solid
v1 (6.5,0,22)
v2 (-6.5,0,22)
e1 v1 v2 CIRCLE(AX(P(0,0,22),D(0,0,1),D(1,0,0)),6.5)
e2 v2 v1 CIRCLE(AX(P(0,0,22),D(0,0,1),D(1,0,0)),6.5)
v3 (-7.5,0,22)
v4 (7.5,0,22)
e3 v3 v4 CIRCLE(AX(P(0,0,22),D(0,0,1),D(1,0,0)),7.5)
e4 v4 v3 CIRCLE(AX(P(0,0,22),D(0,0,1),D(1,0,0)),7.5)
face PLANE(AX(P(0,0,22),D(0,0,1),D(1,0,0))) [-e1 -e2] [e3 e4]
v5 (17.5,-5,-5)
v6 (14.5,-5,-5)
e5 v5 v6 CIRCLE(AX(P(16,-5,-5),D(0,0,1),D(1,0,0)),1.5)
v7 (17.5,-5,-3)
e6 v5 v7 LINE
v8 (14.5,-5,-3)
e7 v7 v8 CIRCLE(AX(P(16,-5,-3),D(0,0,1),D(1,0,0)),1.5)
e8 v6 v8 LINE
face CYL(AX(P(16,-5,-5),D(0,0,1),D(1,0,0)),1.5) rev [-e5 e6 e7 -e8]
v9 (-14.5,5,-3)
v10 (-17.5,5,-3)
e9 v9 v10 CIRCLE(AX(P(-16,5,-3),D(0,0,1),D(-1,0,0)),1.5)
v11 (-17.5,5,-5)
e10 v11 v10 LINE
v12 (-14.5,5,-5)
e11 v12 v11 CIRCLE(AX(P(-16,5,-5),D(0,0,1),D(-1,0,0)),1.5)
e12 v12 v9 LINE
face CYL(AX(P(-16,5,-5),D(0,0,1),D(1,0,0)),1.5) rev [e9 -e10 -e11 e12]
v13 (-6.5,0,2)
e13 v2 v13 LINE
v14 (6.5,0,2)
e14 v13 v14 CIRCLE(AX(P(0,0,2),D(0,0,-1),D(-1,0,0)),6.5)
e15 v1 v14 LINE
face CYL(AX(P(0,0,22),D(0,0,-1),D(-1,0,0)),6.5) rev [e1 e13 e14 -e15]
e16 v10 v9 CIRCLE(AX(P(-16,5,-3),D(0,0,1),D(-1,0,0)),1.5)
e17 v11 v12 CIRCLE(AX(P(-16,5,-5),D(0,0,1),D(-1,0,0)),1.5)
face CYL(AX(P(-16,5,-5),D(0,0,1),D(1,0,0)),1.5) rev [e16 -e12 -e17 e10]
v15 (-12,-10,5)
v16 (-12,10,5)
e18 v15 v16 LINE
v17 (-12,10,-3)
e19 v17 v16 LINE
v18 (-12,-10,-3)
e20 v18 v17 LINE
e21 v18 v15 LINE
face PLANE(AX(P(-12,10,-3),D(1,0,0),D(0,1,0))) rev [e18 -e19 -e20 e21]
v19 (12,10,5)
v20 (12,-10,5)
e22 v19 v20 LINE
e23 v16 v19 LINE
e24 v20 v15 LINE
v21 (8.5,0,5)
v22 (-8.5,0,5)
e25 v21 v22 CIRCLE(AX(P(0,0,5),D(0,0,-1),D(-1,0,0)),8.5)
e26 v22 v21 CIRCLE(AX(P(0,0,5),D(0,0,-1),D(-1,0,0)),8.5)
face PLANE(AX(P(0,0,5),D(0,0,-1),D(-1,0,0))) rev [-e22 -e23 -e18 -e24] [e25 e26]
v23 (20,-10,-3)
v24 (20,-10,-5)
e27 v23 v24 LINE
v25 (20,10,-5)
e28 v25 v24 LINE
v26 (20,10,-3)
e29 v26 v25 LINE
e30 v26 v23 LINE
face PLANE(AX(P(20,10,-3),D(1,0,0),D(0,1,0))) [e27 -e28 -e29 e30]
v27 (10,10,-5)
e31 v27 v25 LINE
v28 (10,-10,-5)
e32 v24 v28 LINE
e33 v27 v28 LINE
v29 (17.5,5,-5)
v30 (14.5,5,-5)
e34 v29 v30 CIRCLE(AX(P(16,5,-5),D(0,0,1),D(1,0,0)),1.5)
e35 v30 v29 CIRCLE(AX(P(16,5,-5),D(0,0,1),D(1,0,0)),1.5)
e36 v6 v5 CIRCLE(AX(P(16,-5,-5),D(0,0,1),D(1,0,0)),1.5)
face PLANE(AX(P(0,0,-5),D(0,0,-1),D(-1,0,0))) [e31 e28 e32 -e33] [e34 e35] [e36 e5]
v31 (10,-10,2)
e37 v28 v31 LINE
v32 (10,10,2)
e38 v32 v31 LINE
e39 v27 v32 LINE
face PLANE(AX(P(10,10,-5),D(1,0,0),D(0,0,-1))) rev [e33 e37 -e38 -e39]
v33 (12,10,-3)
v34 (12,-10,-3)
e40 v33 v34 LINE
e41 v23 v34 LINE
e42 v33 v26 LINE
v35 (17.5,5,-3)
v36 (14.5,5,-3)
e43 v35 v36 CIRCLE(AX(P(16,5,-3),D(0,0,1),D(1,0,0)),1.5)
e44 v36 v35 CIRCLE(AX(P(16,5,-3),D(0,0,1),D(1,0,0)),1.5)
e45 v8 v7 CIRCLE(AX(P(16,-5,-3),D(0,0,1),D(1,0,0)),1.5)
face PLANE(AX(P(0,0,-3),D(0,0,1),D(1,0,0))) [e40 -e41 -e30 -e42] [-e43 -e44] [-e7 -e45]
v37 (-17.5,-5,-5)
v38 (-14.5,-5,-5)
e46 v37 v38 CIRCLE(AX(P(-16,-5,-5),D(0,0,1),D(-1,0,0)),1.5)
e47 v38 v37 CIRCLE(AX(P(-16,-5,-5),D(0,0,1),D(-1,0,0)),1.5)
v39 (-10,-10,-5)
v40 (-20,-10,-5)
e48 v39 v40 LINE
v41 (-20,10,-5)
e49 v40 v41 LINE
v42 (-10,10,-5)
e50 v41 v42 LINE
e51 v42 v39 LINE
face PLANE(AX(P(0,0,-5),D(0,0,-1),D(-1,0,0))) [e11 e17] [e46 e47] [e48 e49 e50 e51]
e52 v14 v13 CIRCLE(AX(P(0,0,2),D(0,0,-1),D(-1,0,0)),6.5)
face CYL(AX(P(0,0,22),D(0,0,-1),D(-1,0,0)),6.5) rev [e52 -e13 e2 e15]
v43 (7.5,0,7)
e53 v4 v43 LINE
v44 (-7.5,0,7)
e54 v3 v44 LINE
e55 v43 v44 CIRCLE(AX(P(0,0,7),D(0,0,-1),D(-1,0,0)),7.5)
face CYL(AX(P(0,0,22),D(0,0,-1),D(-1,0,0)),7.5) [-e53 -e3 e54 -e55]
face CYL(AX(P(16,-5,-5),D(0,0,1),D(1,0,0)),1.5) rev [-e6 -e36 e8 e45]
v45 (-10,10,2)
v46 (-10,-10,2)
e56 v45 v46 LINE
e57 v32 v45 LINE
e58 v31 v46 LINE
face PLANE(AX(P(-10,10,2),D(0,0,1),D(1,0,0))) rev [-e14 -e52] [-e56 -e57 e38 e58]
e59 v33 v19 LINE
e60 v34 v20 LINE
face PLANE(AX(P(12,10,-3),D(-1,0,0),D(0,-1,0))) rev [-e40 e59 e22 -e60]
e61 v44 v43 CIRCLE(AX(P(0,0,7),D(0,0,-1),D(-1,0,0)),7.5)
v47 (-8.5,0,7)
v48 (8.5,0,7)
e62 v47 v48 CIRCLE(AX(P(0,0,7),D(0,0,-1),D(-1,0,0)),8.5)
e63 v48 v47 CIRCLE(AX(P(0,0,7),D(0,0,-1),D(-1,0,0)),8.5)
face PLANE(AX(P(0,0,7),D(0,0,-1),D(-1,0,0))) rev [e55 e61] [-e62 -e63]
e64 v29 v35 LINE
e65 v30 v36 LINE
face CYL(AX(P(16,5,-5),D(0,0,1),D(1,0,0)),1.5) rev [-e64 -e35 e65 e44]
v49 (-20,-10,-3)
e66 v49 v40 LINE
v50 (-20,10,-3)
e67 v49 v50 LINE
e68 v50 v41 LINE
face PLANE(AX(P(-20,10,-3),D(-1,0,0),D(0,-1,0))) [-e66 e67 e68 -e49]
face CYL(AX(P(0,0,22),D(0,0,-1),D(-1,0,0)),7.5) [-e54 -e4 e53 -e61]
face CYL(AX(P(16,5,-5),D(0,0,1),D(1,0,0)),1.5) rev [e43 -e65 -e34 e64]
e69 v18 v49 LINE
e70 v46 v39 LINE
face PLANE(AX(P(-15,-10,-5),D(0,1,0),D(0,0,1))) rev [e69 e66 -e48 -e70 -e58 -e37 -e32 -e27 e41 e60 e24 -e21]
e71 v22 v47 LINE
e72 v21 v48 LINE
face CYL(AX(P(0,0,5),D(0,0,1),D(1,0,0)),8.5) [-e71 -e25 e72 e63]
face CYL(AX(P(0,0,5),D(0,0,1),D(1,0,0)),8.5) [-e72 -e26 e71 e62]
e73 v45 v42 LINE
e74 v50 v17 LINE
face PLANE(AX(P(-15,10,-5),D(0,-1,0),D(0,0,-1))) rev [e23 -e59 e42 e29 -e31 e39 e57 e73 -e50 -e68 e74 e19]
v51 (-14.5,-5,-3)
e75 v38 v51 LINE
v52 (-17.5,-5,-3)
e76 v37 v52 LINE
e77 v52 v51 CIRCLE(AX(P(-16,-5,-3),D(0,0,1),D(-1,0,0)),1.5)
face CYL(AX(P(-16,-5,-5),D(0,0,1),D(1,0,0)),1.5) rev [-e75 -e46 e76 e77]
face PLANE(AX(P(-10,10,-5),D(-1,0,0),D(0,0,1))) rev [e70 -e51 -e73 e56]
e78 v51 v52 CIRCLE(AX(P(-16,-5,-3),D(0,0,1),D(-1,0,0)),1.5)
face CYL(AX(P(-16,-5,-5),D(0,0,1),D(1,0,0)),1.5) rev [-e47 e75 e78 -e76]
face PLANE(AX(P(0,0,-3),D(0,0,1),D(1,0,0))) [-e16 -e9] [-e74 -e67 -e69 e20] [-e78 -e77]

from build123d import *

# Parameters (mm, degrees)
SKETCH1_R           = 7.5
SKETCH1_R_2         = 6.5
BOSS_EXTRUDE1_DEPTH = 22
BOSS_EXTRUDE2_START = 2
SKETCH2_R           = 8.5
SKETCH2_R_2         = 7.5
BOSS_EXTRUDE2_DEPTH = 2
BOSS_EXTRUDE4_START = 2
SKETCH5_R           = 7.5
SKETCH5_R_2         = 6.5
BOSS_EXTRUDE4_DEPTH = 2
BOSS_EXTRUDE5_START = 2
SKETCH6_R           = 8.5
SKETCH6_R_2         = 6.5
BOSS_EXTRUDE5_DEPTH = 2
SKETCH7_W           = 30
SKETCH7_H           = 20
BOSS_EXTRUDE6_DEPTH = 10
SKETCH8_W           = 20
SKETCH8_H           = 7
CUT_EXTRUDE1_DEPTH  = 34.301651611
SKETCH9_W           = 5
SKETCH9_H           = 20
BOSS_EXTRUDE7_DEPTH = 2
SKETCH12_R          = 6.5
CUT_EXTRUDE3_DEPTH  = 31
SKETCH13_W          = 3
SKETCH13_H          = 20
CUT_EXTRUDE4_DEPTH  = 8
SKETCH11_R          = 1.5
CUT_EXTRUDE2_DEPTH  = 34.541019662


with BuildPart() as part:
    # Sketch1 → Boss-Extrude1 (new body)
    with BuildSketch(Plane.XY):
        Circle(SKETCH1_R)
        Circle(SKETCH1_R_2, mode=Mode.SUBTRACT)
    extrude(amount=BOSS_EXTRUDE1_DEPTH)

    # Sketch2 → Boss-Extrude2 (add)
    with BuildSketch(Plane(origin=(0, 0, 7), x_dir=(-1, 0, 0), z_dir=(0, 0, -1)).offset(BOSS_EXTRUDE2_START)):
        Circle(SKETCH2_R)
        Circle(SKETCH2_R_2, mode=Mode.SUBTRACT)
    extrude(amount=-BOSS_EXTRUDE2_DEPTH)

    # Sketch5 → Boss-Extrude4 (add)
    with BuildSketch(Plane(origin=(0, 0, 0), x_dir=(-1, 0, 0), z_dir=(0, 0, -1)).offset(BOSS_EXTRUDE4_START)):
        Circle(SKETCH5_R)
        Circle(SKETCH5_R_2, mode=Mode.SUBTRACT)
    extrude(amount=-BOSS_EXTRUDE4_DEPTH)

    # Sketch6 → Boss-Extrude5 (add)
    with BuildSketch(Plane(origin=(0, 0, -2), x_dir=(-1, 0, 0), z_dir=(0, 0, -1)).offset(BOSS_EXTRUDE5_START)):
        Circle(SKETCH6_R)
        Circle(SKETCH6_R_2, mode=Mode.SUBTRACT)
    extrude(amount=-BOSS_EXTRUDE5_DEPTH)

    # Sketch7 → Boss-Extrude6 (add)
    with BuildSketch(Plane(origin=(0, 0, 5), x_dir=(-1, 0, 0), z_dir=(0, 0, -1))):
        Rectangle(SKETCH7_W, SKETCH7_H)
    extrude(amount=BOSS_EXTRUDE6_DEPTH)

    # Sketch8 → Cut-Extrude1 (cut, through all)
    with BuildSketch(Plane.XZ.offset(10)):
        with Locations((0, -1.5)):
            Rectangle(SKETCH8_W, SKETCH8_H)
    extrude(amount=-CUT_EXTRUDE1_DEPTH, mode=Mode.SUBTRACT)

    # Sketch9 → Boss-Extrude7 (add)
    with BuildSketch(Plane(origin=(0, 0, -5), x_dir=(-1, 0, 0), z_dir=(0, 0, -1))):
        with Locations((-17.5, 0)):
            Rectangle(SKETCH9_W, SKETCH9_H)
        with Locations((17.5, 0)):
            Rectangle(SKETCH9_W, SKETCH9_H)
    extrude(amount=-BOSS_EXTRUDE7_DEPTH)

    # Sketch12 → Cut-Extrude3 (cut, through all)
    with BuildSketch(Plane(origin=(0, 0, 2), x_dir=(-1, 0, 0), z_dir=(0, 0, -1))):
        Circle(SKETCH12_R)
    extrude(amount=-CUT_EXTRUDE3_DEPTH, mode=Mode.SUBTRACT)

    # Sketch13 → Cut-Extrude4 (cut)
    with BuildSketch(Plane.XY.offset(5)):
        with Locations((-13.5, 0)):
            Rectangle(SKETCH13_W, SKETCH13_H)
        with Locations((13.5, 0)):
            Rectangle(SKETCH13_W, SKETCH13_H)
    extrude(amount=-CUT_EXTRUDE4_DEPTH, mode=Mode.SUBTRACT)

    # Sketch11 → Cut-Extrude2 (cut, through all)
    with BuildSketch(Plane.XY.offset(-3)):
        with Locations((16, 5)):
            Circle(SKETCH11_R)
        with Locations((16, -5)):
            Circle(SKETCH11_R)
        with Locations(Location((-16, -5, 0), (0, 0, 180))):
            Circle(SKETCH11_R)
        with Locations(Location((-16, 5, 0), (0, 0, 180))):
            Circle(SKETCH11_R)
    extrude(amount=-CUT_EXTRUDE2_DEPTH, mode=Mode.SUBTRACT)


solid = part.part
